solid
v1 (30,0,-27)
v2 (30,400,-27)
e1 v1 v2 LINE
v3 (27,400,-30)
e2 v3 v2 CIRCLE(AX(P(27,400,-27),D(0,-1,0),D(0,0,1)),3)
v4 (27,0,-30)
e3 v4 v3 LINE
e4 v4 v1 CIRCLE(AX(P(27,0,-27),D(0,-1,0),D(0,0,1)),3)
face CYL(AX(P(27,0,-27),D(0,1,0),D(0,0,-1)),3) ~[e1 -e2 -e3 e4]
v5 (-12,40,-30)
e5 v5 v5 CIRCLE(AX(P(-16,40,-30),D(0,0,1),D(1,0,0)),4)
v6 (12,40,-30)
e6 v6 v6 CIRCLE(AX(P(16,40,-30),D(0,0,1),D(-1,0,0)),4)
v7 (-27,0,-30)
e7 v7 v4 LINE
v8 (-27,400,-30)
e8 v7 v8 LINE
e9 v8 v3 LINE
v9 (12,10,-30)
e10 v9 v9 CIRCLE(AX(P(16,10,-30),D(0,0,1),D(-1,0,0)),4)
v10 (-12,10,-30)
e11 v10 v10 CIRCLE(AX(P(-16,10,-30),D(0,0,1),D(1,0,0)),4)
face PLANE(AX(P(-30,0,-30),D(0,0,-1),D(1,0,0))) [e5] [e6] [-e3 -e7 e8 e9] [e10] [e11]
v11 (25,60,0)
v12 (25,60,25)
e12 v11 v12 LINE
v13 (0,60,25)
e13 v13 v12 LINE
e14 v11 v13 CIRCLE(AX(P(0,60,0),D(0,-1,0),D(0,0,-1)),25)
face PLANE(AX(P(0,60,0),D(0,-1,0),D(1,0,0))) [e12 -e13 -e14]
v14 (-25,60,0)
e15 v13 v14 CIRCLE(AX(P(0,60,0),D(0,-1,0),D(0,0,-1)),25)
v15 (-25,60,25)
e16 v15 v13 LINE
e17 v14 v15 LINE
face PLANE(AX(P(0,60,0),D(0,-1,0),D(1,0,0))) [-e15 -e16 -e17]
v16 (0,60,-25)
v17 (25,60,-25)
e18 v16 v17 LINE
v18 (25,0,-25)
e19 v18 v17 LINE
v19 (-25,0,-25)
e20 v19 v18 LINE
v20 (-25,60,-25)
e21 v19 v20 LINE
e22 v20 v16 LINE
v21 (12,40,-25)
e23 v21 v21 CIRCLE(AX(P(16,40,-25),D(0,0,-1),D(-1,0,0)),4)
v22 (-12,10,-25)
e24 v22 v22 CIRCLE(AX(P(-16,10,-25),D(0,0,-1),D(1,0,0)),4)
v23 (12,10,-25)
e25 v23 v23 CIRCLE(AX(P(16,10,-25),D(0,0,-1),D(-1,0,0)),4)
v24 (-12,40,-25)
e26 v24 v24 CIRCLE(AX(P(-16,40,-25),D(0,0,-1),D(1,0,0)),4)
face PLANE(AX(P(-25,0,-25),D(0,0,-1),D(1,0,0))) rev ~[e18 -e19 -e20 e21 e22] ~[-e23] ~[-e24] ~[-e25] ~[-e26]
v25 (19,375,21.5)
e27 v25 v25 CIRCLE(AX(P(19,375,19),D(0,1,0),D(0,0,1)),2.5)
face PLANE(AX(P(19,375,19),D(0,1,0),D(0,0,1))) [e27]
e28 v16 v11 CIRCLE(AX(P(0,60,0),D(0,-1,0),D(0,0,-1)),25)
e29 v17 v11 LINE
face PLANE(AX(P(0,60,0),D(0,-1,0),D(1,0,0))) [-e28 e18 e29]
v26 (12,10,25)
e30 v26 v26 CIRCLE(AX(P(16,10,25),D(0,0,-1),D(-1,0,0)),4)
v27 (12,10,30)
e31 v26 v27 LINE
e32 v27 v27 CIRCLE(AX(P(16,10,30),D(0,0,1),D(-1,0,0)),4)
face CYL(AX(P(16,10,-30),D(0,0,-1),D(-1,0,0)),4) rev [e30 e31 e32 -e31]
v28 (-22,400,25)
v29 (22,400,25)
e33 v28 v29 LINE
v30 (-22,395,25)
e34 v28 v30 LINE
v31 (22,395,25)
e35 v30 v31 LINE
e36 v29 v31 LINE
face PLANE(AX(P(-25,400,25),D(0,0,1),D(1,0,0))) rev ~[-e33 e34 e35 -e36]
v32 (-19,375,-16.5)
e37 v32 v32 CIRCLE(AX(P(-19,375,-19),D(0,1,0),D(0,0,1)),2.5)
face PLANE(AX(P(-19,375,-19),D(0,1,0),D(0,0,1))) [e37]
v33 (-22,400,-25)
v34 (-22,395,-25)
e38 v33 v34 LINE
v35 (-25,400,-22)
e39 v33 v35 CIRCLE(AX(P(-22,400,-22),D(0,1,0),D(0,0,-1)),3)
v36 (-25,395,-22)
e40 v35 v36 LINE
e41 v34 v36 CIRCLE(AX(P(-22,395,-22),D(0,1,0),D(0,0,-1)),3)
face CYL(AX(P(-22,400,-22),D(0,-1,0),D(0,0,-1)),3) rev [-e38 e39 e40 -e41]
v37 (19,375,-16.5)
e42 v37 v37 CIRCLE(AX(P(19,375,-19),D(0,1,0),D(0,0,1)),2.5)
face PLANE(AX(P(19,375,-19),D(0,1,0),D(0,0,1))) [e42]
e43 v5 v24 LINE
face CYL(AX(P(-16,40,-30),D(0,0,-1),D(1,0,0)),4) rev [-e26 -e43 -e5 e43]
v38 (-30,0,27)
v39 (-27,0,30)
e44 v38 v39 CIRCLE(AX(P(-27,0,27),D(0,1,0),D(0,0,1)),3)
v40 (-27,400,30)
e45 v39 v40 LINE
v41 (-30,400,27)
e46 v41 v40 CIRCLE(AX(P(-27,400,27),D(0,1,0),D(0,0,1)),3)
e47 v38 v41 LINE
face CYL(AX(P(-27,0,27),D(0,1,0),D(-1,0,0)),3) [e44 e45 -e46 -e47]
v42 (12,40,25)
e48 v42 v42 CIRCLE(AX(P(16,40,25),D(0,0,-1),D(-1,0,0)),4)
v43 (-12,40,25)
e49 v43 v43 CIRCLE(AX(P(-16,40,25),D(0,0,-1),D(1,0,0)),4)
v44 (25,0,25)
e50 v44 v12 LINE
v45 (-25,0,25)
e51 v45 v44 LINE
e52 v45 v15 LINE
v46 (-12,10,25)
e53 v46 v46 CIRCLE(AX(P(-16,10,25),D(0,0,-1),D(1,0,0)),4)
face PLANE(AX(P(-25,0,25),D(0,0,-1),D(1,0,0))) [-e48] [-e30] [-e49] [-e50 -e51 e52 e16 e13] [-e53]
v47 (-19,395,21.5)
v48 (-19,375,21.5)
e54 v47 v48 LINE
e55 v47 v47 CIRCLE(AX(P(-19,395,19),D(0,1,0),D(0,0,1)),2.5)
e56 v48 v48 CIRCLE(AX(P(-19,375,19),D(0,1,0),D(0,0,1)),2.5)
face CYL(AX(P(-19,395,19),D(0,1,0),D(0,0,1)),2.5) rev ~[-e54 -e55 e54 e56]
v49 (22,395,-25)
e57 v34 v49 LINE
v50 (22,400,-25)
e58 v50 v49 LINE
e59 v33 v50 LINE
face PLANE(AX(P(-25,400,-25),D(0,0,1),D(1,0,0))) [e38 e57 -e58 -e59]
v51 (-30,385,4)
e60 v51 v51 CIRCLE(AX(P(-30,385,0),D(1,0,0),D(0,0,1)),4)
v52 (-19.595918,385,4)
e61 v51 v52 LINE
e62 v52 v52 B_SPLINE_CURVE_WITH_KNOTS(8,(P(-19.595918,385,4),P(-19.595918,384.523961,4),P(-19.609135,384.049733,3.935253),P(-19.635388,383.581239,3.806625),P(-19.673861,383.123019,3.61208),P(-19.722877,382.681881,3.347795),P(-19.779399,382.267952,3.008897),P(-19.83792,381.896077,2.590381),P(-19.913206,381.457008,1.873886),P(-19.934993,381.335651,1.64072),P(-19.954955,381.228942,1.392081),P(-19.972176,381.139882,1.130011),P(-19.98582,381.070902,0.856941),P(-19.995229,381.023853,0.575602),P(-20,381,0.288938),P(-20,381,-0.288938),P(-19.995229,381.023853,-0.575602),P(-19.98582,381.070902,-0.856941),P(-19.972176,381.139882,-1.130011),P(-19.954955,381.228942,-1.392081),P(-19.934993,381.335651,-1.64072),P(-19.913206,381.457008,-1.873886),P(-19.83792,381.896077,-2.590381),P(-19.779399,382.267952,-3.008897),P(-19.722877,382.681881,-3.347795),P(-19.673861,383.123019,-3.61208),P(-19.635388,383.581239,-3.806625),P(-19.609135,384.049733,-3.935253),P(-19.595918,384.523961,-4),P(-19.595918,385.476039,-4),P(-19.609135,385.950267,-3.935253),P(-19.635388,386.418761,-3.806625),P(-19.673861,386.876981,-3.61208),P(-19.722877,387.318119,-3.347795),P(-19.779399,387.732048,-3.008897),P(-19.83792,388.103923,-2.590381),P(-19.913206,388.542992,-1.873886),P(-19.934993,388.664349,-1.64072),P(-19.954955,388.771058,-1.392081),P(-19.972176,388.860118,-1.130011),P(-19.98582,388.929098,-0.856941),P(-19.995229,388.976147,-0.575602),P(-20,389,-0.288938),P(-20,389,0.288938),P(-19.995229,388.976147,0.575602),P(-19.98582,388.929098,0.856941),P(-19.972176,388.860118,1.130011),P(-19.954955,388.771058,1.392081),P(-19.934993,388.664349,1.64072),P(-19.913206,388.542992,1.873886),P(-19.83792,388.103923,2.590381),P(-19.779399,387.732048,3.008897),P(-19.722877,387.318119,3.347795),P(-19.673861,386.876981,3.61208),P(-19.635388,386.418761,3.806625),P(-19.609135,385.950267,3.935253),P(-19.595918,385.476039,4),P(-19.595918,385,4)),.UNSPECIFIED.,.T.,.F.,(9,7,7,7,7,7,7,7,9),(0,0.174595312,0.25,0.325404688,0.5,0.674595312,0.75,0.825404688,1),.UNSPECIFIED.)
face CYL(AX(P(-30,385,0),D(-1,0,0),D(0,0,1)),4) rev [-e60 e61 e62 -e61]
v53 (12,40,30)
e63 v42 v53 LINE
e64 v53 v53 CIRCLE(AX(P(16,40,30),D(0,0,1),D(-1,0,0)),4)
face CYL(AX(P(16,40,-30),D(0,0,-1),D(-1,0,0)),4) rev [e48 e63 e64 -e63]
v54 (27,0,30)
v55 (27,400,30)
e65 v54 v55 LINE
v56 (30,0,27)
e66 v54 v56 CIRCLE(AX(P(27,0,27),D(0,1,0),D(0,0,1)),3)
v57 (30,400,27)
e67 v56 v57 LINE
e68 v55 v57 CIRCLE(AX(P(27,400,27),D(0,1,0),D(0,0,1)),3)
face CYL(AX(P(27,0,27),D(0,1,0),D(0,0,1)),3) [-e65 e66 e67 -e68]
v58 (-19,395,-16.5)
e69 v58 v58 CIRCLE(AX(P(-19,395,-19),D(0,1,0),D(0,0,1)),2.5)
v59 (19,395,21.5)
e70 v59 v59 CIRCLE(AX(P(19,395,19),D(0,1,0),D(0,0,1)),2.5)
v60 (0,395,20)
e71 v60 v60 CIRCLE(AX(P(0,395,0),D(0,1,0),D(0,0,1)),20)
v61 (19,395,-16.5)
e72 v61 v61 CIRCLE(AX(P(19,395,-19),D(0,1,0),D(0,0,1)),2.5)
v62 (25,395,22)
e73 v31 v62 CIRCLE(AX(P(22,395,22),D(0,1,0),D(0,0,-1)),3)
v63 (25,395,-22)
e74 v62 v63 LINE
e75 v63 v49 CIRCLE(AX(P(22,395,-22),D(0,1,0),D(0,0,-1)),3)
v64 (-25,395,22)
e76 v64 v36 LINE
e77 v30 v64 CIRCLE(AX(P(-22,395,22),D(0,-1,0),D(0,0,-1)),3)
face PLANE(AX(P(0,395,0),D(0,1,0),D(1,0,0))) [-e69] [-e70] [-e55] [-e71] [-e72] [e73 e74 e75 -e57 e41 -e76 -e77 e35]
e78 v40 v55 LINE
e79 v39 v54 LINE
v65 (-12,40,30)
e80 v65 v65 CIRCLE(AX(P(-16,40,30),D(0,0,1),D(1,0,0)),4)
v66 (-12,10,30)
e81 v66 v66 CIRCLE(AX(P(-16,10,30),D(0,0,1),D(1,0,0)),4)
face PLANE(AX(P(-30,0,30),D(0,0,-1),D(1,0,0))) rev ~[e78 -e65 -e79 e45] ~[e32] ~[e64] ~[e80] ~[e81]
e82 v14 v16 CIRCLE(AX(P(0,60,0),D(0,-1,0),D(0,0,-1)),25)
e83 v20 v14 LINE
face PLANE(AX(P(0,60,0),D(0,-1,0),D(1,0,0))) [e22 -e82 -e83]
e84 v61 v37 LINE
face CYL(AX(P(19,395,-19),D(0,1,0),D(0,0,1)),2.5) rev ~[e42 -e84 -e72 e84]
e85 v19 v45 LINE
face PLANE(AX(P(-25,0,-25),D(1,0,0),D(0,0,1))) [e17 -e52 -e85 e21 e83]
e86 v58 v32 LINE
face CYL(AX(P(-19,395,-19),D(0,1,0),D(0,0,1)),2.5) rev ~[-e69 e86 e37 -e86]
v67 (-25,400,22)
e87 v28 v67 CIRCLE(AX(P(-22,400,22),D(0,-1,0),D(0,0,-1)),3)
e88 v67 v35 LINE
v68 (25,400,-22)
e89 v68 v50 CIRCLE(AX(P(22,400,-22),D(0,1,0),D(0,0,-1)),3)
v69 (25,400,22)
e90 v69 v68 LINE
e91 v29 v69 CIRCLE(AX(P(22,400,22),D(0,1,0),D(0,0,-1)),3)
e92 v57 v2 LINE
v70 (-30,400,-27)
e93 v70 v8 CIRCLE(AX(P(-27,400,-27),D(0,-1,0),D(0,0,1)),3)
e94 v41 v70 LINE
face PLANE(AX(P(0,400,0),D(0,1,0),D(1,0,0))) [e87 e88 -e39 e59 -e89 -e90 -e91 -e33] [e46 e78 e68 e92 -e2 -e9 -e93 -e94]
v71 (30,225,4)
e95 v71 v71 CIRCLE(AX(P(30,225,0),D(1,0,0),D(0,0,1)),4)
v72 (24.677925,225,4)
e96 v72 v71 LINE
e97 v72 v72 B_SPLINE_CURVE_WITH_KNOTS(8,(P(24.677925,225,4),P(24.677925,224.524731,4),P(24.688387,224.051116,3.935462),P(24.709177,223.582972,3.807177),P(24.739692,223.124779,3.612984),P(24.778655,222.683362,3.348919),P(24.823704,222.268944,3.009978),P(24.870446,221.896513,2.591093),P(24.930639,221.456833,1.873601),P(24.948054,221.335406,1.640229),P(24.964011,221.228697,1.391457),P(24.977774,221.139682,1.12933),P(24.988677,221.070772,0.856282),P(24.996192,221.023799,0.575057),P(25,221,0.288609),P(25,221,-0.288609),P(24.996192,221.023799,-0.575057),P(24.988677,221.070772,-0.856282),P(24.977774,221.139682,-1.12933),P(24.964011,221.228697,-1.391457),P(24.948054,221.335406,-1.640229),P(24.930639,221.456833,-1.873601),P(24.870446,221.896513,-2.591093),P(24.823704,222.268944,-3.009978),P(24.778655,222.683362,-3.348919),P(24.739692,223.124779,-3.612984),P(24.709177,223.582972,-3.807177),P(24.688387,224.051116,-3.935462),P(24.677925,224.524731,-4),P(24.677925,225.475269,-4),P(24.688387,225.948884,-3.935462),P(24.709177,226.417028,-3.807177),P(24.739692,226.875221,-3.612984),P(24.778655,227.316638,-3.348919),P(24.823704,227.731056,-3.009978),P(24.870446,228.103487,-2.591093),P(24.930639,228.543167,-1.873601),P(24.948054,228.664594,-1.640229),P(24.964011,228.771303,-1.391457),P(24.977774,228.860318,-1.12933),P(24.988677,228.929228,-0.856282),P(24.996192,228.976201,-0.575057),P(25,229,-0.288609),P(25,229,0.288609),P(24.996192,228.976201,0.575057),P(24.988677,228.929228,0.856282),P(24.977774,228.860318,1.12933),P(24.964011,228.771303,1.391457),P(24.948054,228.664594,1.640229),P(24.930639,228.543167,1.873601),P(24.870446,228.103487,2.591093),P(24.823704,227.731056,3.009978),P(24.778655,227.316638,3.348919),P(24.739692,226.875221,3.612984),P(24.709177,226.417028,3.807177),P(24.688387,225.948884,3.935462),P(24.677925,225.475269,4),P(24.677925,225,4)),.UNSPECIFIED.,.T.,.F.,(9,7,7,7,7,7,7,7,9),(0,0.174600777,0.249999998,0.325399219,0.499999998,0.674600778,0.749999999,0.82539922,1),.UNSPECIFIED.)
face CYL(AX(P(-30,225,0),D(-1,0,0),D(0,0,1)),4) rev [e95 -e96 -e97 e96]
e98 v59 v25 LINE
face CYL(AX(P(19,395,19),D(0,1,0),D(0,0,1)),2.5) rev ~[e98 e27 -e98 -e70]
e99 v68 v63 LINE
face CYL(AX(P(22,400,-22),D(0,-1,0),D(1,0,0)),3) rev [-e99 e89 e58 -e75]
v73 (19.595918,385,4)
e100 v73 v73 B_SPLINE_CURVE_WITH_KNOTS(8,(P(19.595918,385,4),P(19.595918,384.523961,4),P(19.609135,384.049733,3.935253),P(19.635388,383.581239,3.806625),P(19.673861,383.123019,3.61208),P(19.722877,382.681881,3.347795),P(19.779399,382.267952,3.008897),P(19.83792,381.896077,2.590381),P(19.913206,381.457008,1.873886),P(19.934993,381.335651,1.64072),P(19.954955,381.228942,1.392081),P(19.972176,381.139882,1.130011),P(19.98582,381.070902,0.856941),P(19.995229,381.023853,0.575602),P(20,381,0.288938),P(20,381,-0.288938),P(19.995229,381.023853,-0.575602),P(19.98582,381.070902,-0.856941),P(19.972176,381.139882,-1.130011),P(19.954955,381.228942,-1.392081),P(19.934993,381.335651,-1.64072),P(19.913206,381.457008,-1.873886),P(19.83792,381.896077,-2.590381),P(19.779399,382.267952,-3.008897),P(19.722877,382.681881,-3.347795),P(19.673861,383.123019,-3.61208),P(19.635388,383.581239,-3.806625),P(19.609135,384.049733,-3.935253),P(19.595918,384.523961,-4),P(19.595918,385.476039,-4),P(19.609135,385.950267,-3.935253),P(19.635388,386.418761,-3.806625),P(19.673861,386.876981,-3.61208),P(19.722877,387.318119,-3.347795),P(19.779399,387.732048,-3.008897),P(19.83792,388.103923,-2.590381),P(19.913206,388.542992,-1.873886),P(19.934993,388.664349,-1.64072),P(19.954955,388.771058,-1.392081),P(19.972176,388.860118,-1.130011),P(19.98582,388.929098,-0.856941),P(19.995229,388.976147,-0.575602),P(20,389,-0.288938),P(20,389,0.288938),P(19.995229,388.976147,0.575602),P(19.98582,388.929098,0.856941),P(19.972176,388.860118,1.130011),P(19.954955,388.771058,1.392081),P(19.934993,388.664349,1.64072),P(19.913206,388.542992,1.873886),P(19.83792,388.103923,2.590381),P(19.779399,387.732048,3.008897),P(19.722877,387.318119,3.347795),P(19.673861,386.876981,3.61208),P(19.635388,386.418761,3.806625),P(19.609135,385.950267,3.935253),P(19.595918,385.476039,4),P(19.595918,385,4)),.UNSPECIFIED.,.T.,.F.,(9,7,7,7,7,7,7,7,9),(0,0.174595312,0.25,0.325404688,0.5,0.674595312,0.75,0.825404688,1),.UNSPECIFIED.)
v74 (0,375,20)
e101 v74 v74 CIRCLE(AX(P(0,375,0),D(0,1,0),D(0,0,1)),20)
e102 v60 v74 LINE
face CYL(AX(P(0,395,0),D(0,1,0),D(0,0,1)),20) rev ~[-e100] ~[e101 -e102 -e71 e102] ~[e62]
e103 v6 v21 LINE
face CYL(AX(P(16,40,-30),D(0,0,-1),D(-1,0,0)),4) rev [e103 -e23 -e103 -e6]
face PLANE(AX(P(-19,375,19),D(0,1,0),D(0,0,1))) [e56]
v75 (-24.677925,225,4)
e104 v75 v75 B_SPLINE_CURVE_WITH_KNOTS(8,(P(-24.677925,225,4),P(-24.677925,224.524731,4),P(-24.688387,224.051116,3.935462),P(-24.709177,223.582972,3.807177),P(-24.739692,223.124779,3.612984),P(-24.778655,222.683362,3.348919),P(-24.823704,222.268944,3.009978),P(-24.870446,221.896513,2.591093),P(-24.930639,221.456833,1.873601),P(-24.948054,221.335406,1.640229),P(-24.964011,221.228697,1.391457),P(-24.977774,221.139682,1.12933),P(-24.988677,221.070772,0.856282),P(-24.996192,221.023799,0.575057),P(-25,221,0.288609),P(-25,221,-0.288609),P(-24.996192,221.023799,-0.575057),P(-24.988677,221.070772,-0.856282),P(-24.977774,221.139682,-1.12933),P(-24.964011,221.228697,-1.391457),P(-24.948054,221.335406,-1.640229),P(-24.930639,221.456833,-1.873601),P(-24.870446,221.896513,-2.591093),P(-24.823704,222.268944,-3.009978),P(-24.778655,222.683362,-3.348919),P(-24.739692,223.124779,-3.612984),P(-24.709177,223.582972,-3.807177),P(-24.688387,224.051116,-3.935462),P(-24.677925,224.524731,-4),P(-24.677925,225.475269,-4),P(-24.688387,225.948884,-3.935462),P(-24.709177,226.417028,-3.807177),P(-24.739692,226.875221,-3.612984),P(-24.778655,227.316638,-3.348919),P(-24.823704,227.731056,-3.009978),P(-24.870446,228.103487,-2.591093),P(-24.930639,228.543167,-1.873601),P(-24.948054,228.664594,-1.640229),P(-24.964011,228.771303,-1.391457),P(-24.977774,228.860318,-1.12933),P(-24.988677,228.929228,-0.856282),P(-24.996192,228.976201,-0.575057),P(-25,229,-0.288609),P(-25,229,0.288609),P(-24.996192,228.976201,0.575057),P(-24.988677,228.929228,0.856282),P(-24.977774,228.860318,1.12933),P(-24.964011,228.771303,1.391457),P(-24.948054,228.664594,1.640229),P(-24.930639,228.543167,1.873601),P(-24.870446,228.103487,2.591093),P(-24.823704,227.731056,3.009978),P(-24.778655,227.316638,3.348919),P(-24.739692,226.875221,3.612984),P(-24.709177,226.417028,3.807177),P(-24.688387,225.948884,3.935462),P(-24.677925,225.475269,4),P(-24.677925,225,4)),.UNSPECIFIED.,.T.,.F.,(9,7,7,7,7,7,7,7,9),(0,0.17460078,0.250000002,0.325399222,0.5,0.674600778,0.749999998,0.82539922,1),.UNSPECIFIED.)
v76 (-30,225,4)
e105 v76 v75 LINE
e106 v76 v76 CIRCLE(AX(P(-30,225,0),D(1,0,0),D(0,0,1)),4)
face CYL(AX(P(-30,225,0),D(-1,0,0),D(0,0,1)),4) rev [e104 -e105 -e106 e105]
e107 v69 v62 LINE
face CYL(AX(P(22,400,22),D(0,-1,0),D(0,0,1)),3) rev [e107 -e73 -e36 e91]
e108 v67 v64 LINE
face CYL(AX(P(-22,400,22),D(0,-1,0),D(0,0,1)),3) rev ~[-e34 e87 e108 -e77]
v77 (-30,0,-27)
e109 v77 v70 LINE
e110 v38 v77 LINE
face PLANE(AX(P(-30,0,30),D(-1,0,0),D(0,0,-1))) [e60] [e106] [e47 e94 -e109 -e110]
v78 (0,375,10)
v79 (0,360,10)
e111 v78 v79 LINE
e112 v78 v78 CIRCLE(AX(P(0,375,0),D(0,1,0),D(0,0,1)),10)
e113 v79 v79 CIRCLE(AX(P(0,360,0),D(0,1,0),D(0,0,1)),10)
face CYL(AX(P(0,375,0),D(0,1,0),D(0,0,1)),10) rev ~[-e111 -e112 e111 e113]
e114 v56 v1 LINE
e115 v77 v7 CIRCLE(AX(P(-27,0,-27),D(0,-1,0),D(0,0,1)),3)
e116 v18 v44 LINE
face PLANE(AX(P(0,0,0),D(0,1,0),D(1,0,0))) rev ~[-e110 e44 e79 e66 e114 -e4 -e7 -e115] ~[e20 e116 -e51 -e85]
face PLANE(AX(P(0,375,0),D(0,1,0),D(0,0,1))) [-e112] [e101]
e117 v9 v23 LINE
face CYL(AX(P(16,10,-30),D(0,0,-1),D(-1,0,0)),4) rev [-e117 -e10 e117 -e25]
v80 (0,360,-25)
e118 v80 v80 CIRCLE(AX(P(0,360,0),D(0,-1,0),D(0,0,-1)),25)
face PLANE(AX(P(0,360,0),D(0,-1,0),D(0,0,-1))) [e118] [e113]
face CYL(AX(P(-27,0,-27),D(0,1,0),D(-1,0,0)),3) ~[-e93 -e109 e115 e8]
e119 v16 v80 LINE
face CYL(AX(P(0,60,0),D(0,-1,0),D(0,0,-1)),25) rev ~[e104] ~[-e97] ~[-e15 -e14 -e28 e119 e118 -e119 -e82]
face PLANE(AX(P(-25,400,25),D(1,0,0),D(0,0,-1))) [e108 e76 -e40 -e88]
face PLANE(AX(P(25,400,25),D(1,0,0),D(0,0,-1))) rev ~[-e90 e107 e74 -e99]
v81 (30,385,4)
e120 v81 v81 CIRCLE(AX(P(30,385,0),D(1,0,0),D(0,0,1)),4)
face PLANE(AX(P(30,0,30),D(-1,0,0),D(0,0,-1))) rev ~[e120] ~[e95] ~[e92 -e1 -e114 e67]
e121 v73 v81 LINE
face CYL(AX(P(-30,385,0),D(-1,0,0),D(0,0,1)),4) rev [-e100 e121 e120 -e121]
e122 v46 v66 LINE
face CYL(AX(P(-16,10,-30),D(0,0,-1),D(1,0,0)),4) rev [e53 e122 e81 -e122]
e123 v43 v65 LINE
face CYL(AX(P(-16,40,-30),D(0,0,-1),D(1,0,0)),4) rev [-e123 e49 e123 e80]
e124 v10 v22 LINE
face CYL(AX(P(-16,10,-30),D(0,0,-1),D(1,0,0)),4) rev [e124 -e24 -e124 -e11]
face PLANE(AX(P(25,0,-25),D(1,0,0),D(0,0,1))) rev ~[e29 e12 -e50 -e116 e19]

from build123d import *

# Parameters (mm, degrees)
SKETCH1_W               = 60
SKETCH1_H               = 60
BOSS_EXTRUDE1_DEPTH     = 400
SKETCH2_W               = 50
SKETCH2_H               = 50
CUT_EXTRUDE1_DEPTH      = 5
SKETCH3_R               = 20
CUT_EXTRUDE2_DEPTH      = 20
SKETCH4_R               = 10
CUT_EXTRUDE3_DEPTH      = 15
FILLET1_R               = 3
CUT_EXTRUDE4_DEPTH      = 30
CUT_EXTRUDE4_DEPTH_BACK = 30
SKETCH5_R               = 4
SKETCH6_W               = 50
SKETCH6_H               = 50
CUT_EXTRUDE5_DEPTH      = 60
SKETCH7_R               = 25
CUT_EXTRUDE6_DEPTH      = 300
CUT_EXTRUDE7_DEPTH      = 30
CUT_EXTRUDE7_DEPTH_BACK = 30
SKETCH8_R               = 4
CUT_EXTRUDE9_DEPTH      = 30
CUT_EXTRUDE9_DEPTH_BACK = 30
SKETCH10_R              = 4
FILLET2_R               = 3
SKETCH11_R              = 2.5
CUT_EXTRUDE11_DEPTH     = 20


with BuildPart() as part:
    # Sketch1 → Boss-Extrude1 (new body)
    with BuildSketch(Plane(origin=(0, 0, 0), x_dir=(1, 0, 0), z_dir=(0, 1, 0))):
        Rectangle(SKETCH1_W, SKETCH1_H)
    extrude(amount=BOSS_EXTRUDE1_DEPTH)

    # Sketch2 → Cut-Extrude1 (cut)
    with BuildSketch(Plane(origin=(0, 400, 0), x_dir=(1, 0, 0), z_dir=(0, 1, 0))):
        Rectangle(SKETCH2_W, SKETCH2_H)
    extrude(amount=-CUT_EXTRUDE1_DEPTH, mode=Mode.SUBTRACT)

    # Sketch3 → Cut-Extrude2 (cut)
    with BuildSketch(Plane(origin=(0, 395, 0), x_dir=(1, 0, 0), z_dir=(0, 1, 0))):
        with Locations(Location((0, 0, 0), (0, 0, 270))):
            Circle(SKETCH3_R)
    extrude(amount=-CUT_EXTRUDE2_DEPTH, mode=Mode.SUBTRACT)

    # Sketch4 → Cut-Extrude3 (cut)
    with BuildSketch(Plane(origin=(0, 375, 0), x_dir=(1, 0, 0), z_dir=(0, 1, 0))):
        with Locations(Location((0, 0, 0), (0, 0, 270))):
            Circle(SKETCH4_R)
    extrude(amount=-CUT_EXTRUDE3_DEPTH, mode=Mode.SUBTRACT)

    # Fillet1
    fillet1_edges = [part.edges().sort_by_distance(p)[0] for p in [
        (-30, 200, -30),
        (-30, 200, 30),
        (30, 200, 30),
        (30, 200, -30),
    ]]
    fillet(fillet1_edges, radius=FILLET1_R)

    # Sketch5 → Cut-Extrude4 (cut, two sides: drawn at the far end of the back side and taken through both)
    with BuildSketch(Plane(origin=(0, 0, 0), x_dir=(0, 0, -1), z_dir=(1, 0, 0)).offset(-CUT_EXTRUDE4_DEPTH_BACK)):
        with Locations(Location((0, 385, 0), (0, 0, 180))):
            Circle(SKETCH5_R)
    extrude(amount=CUT_EXTRUDE4_DEPTH + CUT_EXTRUDE4_DEPTH_BACK, mode=Mode.SUBTRACT)

    # Sketch6 → Cut-Extrude5 (cut)
    with BuildSketch(Plane.XZ):
        Rectangle(SKETCH6_W, SKETCH6_H)
    extrude(amount=-CUT_EXTRUDE5_DEPTH, mode=Mode.SUBTRACT)

    # Sketch7 → Cut-Extrude6 (cut)
    with BuildSketch(Plane.XZ.offset(-60)):
        with Locations(Location((0, 0, 0), (0, 0, 270))):
            Circle(SKETCH7_R)
    extrude(amount=-CUT_EXTRUDE6_DEPTH, mode=Mode.SUBTRACT)

    # Sketch8 → Cut-Extrude7 (cut, two sides: drawn at the far end of the back side and taken through both)
    with BuildSketch(Plane(origin=(0, 0, 0), x_dir=(0, 0, -1), z_dir=(1, 0, 0)).offset(-CUT_EXTRUDE7_DEPTH_BACK)):
        with Locations(Location((0, 225, 0), (0, 0, 180))):
            Circle(SKETCH8_R)
    extrude(amount=CUT_EXTRUDE7_DEPTH + CUT_EXTRUDE7_DEPTH_BACK, mode=Mode.SUBTRACT)

    # Sketch10 → Cut-Extrude9 (cut, two sides: drawn at the far end of the back side and taken through both)
    with BuildSketch(Plane.XY.offset(-CUT_EXTRUDE9_DEPTH_BACK)):
        with Locations((-16, 40)):
            Circle(SKETCH10_R)
        with Locations((-16, 10)):
            Circle(SKETCH10_R)
        with Locations(Location((16, 10, 0), (0, 0, 180))):
            Circle(SKETCH10_R)
        with Locations(Location((16, 40, 0), (0, 0, 180))):
            Circle(SKETCH10_R)
    extrude(amount=CUT_EXTRUDE9_DEPTH + CUT_EXTRUDE9_DEPTH_BACK, mode=Mode.SUBTRACT)

    # Fillet2
    fillet2_edges = [part.edges().sort_by_distance(p)[0] for p in [
        (25, 397.5, -25),
        (25, 397.5, 25),
        (-25, 397.5, 25),
        (-25, 397.5, -25),
    ]]
    fillet(fillet2_edges, radius=FILLET2_R)

    # Sketch11 → Cut-Extrude11 (cut)
    with BuildSketch(Plane(origin=(0, 395, 0), x_dir=(1, 0, 0), z_dir=(0, 1, 0))):
        with Locations(Location((-19, 19, 0), (0, 0, 270))):
            Circle(SKETCH11_R)
        with Locations(Location((19, 19, 0), (0, 0, 270))):
            Circle(SKETCH11_R)
        with Locations(Location((-19, -19, 0), (0, 0, 270))):
            Circle(SKETCH11_R)
        with Locations(Location((19, -19, 0), (0, 0, 270))):
            Circle(SKETCH11_R)
    extrude(amount=-CUT_EXTRUDE11_DEPTH, mode=Mode.SUBTRACT)


solid = part.part
